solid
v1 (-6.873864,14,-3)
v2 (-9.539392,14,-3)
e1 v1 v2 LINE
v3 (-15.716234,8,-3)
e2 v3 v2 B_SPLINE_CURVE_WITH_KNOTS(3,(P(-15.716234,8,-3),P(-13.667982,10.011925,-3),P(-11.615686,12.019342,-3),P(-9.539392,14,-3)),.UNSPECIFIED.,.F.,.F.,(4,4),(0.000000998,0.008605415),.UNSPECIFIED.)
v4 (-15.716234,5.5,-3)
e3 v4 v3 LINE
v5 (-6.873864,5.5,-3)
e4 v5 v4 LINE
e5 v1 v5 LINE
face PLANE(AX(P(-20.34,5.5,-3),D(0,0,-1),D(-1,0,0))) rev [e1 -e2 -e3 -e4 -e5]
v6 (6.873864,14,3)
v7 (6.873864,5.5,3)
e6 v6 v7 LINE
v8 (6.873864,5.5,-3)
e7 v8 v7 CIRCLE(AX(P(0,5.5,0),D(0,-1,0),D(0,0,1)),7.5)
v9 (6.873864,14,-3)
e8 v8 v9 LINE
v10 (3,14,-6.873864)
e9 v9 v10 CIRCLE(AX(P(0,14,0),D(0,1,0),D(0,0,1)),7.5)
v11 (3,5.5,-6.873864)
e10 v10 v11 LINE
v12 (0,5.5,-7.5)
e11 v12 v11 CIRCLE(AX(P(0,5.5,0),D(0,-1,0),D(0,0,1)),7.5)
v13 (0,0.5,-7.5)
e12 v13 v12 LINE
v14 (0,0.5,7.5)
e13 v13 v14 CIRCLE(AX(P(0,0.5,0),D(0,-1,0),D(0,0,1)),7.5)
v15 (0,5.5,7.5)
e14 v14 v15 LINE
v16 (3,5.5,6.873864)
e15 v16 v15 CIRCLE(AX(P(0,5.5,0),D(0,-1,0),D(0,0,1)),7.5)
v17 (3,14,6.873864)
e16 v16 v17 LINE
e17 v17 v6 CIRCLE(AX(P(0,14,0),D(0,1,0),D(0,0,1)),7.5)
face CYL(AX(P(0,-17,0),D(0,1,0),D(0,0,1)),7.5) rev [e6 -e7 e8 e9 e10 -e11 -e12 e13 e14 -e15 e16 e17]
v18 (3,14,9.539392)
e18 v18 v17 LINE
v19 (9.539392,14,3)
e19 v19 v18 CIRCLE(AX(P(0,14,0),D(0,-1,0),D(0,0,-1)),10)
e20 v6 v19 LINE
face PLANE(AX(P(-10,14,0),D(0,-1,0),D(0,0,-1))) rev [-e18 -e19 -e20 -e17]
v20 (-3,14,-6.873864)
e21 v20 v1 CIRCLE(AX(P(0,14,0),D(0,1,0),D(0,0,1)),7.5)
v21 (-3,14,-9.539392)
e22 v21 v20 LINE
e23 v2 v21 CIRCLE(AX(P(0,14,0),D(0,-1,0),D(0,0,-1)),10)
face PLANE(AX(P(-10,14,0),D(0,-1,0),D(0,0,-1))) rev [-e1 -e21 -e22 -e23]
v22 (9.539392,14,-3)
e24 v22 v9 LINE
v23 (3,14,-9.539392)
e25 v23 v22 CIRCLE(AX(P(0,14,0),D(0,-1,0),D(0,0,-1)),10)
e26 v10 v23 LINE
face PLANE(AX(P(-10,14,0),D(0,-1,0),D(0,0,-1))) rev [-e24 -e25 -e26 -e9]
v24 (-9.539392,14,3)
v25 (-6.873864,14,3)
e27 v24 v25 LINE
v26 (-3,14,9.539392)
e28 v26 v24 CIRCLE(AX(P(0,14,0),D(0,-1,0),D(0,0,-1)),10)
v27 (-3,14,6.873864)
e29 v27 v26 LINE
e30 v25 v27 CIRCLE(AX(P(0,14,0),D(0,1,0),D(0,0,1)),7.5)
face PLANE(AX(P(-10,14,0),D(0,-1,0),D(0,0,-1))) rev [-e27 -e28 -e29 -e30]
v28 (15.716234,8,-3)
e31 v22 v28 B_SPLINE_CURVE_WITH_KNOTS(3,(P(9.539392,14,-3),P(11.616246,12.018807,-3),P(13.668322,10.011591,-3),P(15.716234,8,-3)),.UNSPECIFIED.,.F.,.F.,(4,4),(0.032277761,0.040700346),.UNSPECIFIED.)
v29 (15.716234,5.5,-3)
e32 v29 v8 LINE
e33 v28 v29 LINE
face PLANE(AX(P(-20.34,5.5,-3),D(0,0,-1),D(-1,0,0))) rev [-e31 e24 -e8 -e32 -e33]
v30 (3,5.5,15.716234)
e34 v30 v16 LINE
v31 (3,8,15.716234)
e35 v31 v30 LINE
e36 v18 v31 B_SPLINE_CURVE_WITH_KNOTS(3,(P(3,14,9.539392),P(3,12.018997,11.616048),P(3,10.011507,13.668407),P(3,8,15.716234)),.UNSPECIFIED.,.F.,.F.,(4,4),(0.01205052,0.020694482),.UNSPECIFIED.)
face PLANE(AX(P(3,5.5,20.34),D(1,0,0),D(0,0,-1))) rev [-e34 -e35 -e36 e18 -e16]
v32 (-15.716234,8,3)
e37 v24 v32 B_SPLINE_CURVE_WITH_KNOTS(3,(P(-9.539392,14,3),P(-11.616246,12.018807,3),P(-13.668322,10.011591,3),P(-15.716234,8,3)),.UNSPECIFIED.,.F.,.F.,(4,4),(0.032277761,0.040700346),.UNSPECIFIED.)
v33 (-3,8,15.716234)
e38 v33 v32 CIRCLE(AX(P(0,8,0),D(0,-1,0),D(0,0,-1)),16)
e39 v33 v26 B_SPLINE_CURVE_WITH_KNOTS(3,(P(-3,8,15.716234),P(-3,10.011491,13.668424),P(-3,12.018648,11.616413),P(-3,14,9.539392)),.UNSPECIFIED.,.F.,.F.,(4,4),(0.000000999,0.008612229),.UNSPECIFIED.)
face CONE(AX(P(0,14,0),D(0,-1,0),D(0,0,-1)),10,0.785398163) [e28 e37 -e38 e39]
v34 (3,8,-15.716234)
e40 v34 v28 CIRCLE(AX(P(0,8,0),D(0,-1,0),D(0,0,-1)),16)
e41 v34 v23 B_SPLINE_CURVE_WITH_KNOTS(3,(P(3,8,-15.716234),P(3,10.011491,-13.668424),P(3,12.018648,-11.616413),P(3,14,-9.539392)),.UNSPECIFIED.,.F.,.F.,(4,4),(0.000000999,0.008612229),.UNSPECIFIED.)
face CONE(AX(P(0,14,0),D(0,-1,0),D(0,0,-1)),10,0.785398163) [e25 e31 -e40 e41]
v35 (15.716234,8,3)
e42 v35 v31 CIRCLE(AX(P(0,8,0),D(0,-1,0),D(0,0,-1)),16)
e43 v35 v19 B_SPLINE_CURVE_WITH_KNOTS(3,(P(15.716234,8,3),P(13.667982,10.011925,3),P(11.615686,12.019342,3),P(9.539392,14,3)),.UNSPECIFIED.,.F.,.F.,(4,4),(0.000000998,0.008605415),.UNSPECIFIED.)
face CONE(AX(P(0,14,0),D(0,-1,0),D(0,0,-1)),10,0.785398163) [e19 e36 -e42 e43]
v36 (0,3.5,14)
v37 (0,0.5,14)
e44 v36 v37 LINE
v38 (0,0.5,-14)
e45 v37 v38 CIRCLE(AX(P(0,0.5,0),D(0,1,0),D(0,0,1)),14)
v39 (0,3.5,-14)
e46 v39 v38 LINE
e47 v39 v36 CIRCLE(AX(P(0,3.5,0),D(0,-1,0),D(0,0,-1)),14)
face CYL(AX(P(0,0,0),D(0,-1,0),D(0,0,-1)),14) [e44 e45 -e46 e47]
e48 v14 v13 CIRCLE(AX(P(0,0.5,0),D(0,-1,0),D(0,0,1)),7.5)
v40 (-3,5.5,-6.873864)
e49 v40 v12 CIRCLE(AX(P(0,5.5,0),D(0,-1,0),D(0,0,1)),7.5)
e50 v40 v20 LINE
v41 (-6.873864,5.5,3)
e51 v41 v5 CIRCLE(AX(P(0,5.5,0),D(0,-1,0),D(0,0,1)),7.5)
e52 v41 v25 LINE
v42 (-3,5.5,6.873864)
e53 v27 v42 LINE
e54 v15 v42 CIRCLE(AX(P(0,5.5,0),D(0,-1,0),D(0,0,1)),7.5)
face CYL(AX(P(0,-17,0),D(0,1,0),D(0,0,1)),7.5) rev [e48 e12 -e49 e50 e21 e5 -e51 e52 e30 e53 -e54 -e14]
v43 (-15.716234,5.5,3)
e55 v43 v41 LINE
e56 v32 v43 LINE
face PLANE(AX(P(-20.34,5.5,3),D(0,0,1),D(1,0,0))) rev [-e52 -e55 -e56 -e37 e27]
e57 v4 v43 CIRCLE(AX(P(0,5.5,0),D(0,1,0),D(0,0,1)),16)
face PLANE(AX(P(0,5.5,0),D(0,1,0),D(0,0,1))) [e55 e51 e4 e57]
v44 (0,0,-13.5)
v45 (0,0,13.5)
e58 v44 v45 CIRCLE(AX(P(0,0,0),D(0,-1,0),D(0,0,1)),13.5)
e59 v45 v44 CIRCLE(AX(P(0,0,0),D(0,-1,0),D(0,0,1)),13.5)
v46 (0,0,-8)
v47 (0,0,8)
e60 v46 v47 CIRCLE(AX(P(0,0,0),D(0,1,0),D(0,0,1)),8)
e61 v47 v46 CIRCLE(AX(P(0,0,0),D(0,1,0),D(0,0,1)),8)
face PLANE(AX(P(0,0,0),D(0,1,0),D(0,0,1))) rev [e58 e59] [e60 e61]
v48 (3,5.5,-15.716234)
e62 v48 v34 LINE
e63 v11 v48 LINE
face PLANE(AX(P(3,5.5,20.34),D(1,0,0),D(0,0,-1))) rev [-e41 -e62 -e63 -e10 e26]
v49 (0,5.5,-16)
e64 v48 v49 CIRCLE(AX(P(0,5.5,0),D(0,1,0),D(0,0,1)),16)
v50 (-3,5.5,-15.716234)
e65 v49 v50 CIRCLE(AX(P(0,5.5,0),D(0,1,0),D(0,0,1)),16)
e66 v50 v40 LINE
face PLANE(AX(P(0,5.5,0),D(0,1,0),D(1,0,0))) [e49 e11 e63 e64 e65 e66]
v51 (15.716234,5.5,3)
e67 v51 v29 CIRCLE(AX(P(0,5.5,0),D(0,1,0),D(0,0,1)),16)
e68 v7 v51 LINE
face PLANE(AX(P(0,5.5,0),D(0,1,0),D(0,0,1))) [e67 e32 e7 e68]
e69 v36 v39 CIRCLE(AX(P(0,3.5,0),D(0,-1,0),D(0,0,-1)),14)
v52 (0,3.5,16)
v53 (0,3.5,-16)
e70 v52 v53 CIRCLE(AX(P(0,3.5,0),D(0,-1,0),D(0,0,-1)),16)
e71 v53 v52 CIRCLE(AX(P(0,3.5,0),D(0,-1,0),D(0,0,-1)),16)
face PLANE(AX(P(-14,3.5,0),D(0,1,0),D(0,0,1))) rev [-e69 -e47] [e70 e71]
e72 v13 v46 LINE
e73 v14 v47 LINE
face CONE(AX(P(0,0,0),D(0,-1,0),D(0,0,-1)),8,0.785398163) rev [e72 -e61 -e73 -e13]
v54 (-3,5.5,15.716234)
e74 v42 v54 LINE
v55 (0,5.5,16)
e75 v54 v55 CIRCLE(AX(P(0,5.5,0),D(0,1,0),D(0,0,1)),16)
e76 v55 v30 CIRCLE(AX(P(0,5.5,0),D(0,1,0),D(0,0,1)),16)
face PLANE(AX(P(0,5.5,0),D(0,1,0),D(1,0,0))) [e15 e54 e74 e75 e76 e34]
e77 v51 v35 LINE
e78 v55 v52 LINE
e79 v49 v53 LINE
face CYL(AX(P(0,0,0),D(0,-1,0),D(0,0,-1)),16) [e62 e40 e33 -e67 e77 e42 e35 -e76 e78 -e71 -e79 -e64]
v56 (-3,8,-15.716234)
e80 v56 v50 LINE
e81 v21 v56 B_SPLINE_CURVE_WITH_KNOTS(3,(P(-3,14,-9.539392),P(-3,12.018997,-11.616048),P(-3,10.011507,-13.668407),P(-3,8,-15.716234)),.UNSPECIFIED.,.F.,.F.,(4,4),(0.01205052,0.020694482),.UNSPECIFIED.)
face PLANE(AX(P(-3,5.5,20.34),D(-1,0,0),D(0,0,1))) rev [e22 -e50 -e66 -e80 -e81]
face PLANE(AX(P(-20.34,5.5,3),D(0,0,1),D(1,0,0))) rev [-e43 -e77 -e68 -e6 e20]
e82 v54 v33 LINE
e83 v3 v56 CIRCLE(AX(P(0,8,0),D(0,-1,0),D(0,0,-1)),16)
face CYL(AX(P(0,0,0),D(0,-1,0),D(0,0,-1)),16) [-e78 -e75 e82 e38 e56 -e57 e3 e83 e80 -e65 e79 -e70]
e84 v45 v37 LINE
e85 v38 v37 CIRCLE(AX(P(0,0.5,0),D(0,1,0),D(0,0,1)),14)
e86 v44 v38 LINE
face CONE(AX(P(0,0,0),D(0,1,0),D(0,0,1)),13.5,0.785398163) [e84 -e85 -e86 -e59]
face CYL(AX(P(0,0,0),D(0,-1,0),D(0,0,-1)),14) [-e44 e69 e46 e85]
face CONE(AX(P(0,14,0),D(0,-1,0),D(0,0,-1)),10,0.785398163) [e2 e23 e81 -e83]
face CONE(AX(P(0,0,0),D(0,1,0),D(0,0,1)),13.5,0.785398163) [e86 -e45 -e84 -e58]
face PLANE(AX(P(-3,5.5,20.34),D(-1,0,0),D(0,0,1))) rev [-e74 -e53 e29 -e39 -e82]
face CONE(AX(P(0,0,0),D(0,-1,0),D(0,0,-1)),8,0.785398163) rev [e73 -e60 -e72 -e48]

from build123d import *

# Parameters (mm, degrees)
SKETCH2_R          = 7.5
CUT_EXTRUDE1_DEPTH = 31
SKETCH3_W          = 40.68
SKETCH3_H          = 6
CUT_EXTRUDE2_DEPTH = 8.5
CIRPATTERN1_COUNT  = 4
CHAMFER1_SIZE      = 0.5
CHAMFER2_SIZE      = 0.5


with BuildPart() as part:
    # Sketch1 → Revolve1 (revolve)
    with BuildSketch(Plane.XY, mode=Mode.PRIVATE) as revolve1_sk:
        Polygon((0, 0), (-14, 0), (-14, 3.5), (-16, 3.5), (-16, 8), (-10, 14), (0, 14), align=None)
    revolve(revolve1_sk.sketch.rotate(Axis((0, 0, 0), (0, 1, 0)), 270), axis=Axis((0, 0, 0), (0, 1, 0)))

    # Sketch2 → Cut-Extrude1 (cut)
    with BuildSketch(Plane(origin=(0, 14, 0), x_dir=(1, 0, 0), z_dir=(0, 1, 0))):
        with Locations(Location((0, 0, 0), (0, 0, 270))):
            Circle(SKETCH2_R)
    extrude(amount=-CUT_EXTRUDE1_DEPTH, mode=Mode.SUBTRACT)

    # Sketch3 → Cut-Extrude2 (cut)
    with BuildSketch(Plane(origin=(0, 14, 0), x_dir=(1, 0, 0), z_dir=(0, 1, 0))):
        Rectangle(SKETCH3_W, SKETCH3_H)
    cut_extrude2 = extrude(amount=-CUT_EXTRUDE2_DEPTH, mode=Mode.SUBTRACT)

    # CirPattern1: Cut-Extrude2 ×4 about axis
    cirpattern1_axis = Axis((0, -17, 0), (0, 1, 0))
    for i in range(1, CIRPATTERN1_COUNT):
        add(cut_extrude2.rotate(cirpattern1_axis, i * 360 / CIRPATTERN1_COUNT), mode=Mode.SUBTRACT)

    # Chamfer1
    chamfer1_edges = [part.edges().sort_by_distance(p)[0] for p in [
        (0, 0, 14),
    ]]
    chamfer(chamfer1_edges, length=CHAMFER1_SIZE)

    # Chamfer2
    chamfer2_edges = [part.edges().sort_by_distance(p)[0] for p in [
        (0, 0, -7.5),
    ]]
    chamfer(chamfer2_edges, length=CHAMFER2_SIZE)


solid = part.part
